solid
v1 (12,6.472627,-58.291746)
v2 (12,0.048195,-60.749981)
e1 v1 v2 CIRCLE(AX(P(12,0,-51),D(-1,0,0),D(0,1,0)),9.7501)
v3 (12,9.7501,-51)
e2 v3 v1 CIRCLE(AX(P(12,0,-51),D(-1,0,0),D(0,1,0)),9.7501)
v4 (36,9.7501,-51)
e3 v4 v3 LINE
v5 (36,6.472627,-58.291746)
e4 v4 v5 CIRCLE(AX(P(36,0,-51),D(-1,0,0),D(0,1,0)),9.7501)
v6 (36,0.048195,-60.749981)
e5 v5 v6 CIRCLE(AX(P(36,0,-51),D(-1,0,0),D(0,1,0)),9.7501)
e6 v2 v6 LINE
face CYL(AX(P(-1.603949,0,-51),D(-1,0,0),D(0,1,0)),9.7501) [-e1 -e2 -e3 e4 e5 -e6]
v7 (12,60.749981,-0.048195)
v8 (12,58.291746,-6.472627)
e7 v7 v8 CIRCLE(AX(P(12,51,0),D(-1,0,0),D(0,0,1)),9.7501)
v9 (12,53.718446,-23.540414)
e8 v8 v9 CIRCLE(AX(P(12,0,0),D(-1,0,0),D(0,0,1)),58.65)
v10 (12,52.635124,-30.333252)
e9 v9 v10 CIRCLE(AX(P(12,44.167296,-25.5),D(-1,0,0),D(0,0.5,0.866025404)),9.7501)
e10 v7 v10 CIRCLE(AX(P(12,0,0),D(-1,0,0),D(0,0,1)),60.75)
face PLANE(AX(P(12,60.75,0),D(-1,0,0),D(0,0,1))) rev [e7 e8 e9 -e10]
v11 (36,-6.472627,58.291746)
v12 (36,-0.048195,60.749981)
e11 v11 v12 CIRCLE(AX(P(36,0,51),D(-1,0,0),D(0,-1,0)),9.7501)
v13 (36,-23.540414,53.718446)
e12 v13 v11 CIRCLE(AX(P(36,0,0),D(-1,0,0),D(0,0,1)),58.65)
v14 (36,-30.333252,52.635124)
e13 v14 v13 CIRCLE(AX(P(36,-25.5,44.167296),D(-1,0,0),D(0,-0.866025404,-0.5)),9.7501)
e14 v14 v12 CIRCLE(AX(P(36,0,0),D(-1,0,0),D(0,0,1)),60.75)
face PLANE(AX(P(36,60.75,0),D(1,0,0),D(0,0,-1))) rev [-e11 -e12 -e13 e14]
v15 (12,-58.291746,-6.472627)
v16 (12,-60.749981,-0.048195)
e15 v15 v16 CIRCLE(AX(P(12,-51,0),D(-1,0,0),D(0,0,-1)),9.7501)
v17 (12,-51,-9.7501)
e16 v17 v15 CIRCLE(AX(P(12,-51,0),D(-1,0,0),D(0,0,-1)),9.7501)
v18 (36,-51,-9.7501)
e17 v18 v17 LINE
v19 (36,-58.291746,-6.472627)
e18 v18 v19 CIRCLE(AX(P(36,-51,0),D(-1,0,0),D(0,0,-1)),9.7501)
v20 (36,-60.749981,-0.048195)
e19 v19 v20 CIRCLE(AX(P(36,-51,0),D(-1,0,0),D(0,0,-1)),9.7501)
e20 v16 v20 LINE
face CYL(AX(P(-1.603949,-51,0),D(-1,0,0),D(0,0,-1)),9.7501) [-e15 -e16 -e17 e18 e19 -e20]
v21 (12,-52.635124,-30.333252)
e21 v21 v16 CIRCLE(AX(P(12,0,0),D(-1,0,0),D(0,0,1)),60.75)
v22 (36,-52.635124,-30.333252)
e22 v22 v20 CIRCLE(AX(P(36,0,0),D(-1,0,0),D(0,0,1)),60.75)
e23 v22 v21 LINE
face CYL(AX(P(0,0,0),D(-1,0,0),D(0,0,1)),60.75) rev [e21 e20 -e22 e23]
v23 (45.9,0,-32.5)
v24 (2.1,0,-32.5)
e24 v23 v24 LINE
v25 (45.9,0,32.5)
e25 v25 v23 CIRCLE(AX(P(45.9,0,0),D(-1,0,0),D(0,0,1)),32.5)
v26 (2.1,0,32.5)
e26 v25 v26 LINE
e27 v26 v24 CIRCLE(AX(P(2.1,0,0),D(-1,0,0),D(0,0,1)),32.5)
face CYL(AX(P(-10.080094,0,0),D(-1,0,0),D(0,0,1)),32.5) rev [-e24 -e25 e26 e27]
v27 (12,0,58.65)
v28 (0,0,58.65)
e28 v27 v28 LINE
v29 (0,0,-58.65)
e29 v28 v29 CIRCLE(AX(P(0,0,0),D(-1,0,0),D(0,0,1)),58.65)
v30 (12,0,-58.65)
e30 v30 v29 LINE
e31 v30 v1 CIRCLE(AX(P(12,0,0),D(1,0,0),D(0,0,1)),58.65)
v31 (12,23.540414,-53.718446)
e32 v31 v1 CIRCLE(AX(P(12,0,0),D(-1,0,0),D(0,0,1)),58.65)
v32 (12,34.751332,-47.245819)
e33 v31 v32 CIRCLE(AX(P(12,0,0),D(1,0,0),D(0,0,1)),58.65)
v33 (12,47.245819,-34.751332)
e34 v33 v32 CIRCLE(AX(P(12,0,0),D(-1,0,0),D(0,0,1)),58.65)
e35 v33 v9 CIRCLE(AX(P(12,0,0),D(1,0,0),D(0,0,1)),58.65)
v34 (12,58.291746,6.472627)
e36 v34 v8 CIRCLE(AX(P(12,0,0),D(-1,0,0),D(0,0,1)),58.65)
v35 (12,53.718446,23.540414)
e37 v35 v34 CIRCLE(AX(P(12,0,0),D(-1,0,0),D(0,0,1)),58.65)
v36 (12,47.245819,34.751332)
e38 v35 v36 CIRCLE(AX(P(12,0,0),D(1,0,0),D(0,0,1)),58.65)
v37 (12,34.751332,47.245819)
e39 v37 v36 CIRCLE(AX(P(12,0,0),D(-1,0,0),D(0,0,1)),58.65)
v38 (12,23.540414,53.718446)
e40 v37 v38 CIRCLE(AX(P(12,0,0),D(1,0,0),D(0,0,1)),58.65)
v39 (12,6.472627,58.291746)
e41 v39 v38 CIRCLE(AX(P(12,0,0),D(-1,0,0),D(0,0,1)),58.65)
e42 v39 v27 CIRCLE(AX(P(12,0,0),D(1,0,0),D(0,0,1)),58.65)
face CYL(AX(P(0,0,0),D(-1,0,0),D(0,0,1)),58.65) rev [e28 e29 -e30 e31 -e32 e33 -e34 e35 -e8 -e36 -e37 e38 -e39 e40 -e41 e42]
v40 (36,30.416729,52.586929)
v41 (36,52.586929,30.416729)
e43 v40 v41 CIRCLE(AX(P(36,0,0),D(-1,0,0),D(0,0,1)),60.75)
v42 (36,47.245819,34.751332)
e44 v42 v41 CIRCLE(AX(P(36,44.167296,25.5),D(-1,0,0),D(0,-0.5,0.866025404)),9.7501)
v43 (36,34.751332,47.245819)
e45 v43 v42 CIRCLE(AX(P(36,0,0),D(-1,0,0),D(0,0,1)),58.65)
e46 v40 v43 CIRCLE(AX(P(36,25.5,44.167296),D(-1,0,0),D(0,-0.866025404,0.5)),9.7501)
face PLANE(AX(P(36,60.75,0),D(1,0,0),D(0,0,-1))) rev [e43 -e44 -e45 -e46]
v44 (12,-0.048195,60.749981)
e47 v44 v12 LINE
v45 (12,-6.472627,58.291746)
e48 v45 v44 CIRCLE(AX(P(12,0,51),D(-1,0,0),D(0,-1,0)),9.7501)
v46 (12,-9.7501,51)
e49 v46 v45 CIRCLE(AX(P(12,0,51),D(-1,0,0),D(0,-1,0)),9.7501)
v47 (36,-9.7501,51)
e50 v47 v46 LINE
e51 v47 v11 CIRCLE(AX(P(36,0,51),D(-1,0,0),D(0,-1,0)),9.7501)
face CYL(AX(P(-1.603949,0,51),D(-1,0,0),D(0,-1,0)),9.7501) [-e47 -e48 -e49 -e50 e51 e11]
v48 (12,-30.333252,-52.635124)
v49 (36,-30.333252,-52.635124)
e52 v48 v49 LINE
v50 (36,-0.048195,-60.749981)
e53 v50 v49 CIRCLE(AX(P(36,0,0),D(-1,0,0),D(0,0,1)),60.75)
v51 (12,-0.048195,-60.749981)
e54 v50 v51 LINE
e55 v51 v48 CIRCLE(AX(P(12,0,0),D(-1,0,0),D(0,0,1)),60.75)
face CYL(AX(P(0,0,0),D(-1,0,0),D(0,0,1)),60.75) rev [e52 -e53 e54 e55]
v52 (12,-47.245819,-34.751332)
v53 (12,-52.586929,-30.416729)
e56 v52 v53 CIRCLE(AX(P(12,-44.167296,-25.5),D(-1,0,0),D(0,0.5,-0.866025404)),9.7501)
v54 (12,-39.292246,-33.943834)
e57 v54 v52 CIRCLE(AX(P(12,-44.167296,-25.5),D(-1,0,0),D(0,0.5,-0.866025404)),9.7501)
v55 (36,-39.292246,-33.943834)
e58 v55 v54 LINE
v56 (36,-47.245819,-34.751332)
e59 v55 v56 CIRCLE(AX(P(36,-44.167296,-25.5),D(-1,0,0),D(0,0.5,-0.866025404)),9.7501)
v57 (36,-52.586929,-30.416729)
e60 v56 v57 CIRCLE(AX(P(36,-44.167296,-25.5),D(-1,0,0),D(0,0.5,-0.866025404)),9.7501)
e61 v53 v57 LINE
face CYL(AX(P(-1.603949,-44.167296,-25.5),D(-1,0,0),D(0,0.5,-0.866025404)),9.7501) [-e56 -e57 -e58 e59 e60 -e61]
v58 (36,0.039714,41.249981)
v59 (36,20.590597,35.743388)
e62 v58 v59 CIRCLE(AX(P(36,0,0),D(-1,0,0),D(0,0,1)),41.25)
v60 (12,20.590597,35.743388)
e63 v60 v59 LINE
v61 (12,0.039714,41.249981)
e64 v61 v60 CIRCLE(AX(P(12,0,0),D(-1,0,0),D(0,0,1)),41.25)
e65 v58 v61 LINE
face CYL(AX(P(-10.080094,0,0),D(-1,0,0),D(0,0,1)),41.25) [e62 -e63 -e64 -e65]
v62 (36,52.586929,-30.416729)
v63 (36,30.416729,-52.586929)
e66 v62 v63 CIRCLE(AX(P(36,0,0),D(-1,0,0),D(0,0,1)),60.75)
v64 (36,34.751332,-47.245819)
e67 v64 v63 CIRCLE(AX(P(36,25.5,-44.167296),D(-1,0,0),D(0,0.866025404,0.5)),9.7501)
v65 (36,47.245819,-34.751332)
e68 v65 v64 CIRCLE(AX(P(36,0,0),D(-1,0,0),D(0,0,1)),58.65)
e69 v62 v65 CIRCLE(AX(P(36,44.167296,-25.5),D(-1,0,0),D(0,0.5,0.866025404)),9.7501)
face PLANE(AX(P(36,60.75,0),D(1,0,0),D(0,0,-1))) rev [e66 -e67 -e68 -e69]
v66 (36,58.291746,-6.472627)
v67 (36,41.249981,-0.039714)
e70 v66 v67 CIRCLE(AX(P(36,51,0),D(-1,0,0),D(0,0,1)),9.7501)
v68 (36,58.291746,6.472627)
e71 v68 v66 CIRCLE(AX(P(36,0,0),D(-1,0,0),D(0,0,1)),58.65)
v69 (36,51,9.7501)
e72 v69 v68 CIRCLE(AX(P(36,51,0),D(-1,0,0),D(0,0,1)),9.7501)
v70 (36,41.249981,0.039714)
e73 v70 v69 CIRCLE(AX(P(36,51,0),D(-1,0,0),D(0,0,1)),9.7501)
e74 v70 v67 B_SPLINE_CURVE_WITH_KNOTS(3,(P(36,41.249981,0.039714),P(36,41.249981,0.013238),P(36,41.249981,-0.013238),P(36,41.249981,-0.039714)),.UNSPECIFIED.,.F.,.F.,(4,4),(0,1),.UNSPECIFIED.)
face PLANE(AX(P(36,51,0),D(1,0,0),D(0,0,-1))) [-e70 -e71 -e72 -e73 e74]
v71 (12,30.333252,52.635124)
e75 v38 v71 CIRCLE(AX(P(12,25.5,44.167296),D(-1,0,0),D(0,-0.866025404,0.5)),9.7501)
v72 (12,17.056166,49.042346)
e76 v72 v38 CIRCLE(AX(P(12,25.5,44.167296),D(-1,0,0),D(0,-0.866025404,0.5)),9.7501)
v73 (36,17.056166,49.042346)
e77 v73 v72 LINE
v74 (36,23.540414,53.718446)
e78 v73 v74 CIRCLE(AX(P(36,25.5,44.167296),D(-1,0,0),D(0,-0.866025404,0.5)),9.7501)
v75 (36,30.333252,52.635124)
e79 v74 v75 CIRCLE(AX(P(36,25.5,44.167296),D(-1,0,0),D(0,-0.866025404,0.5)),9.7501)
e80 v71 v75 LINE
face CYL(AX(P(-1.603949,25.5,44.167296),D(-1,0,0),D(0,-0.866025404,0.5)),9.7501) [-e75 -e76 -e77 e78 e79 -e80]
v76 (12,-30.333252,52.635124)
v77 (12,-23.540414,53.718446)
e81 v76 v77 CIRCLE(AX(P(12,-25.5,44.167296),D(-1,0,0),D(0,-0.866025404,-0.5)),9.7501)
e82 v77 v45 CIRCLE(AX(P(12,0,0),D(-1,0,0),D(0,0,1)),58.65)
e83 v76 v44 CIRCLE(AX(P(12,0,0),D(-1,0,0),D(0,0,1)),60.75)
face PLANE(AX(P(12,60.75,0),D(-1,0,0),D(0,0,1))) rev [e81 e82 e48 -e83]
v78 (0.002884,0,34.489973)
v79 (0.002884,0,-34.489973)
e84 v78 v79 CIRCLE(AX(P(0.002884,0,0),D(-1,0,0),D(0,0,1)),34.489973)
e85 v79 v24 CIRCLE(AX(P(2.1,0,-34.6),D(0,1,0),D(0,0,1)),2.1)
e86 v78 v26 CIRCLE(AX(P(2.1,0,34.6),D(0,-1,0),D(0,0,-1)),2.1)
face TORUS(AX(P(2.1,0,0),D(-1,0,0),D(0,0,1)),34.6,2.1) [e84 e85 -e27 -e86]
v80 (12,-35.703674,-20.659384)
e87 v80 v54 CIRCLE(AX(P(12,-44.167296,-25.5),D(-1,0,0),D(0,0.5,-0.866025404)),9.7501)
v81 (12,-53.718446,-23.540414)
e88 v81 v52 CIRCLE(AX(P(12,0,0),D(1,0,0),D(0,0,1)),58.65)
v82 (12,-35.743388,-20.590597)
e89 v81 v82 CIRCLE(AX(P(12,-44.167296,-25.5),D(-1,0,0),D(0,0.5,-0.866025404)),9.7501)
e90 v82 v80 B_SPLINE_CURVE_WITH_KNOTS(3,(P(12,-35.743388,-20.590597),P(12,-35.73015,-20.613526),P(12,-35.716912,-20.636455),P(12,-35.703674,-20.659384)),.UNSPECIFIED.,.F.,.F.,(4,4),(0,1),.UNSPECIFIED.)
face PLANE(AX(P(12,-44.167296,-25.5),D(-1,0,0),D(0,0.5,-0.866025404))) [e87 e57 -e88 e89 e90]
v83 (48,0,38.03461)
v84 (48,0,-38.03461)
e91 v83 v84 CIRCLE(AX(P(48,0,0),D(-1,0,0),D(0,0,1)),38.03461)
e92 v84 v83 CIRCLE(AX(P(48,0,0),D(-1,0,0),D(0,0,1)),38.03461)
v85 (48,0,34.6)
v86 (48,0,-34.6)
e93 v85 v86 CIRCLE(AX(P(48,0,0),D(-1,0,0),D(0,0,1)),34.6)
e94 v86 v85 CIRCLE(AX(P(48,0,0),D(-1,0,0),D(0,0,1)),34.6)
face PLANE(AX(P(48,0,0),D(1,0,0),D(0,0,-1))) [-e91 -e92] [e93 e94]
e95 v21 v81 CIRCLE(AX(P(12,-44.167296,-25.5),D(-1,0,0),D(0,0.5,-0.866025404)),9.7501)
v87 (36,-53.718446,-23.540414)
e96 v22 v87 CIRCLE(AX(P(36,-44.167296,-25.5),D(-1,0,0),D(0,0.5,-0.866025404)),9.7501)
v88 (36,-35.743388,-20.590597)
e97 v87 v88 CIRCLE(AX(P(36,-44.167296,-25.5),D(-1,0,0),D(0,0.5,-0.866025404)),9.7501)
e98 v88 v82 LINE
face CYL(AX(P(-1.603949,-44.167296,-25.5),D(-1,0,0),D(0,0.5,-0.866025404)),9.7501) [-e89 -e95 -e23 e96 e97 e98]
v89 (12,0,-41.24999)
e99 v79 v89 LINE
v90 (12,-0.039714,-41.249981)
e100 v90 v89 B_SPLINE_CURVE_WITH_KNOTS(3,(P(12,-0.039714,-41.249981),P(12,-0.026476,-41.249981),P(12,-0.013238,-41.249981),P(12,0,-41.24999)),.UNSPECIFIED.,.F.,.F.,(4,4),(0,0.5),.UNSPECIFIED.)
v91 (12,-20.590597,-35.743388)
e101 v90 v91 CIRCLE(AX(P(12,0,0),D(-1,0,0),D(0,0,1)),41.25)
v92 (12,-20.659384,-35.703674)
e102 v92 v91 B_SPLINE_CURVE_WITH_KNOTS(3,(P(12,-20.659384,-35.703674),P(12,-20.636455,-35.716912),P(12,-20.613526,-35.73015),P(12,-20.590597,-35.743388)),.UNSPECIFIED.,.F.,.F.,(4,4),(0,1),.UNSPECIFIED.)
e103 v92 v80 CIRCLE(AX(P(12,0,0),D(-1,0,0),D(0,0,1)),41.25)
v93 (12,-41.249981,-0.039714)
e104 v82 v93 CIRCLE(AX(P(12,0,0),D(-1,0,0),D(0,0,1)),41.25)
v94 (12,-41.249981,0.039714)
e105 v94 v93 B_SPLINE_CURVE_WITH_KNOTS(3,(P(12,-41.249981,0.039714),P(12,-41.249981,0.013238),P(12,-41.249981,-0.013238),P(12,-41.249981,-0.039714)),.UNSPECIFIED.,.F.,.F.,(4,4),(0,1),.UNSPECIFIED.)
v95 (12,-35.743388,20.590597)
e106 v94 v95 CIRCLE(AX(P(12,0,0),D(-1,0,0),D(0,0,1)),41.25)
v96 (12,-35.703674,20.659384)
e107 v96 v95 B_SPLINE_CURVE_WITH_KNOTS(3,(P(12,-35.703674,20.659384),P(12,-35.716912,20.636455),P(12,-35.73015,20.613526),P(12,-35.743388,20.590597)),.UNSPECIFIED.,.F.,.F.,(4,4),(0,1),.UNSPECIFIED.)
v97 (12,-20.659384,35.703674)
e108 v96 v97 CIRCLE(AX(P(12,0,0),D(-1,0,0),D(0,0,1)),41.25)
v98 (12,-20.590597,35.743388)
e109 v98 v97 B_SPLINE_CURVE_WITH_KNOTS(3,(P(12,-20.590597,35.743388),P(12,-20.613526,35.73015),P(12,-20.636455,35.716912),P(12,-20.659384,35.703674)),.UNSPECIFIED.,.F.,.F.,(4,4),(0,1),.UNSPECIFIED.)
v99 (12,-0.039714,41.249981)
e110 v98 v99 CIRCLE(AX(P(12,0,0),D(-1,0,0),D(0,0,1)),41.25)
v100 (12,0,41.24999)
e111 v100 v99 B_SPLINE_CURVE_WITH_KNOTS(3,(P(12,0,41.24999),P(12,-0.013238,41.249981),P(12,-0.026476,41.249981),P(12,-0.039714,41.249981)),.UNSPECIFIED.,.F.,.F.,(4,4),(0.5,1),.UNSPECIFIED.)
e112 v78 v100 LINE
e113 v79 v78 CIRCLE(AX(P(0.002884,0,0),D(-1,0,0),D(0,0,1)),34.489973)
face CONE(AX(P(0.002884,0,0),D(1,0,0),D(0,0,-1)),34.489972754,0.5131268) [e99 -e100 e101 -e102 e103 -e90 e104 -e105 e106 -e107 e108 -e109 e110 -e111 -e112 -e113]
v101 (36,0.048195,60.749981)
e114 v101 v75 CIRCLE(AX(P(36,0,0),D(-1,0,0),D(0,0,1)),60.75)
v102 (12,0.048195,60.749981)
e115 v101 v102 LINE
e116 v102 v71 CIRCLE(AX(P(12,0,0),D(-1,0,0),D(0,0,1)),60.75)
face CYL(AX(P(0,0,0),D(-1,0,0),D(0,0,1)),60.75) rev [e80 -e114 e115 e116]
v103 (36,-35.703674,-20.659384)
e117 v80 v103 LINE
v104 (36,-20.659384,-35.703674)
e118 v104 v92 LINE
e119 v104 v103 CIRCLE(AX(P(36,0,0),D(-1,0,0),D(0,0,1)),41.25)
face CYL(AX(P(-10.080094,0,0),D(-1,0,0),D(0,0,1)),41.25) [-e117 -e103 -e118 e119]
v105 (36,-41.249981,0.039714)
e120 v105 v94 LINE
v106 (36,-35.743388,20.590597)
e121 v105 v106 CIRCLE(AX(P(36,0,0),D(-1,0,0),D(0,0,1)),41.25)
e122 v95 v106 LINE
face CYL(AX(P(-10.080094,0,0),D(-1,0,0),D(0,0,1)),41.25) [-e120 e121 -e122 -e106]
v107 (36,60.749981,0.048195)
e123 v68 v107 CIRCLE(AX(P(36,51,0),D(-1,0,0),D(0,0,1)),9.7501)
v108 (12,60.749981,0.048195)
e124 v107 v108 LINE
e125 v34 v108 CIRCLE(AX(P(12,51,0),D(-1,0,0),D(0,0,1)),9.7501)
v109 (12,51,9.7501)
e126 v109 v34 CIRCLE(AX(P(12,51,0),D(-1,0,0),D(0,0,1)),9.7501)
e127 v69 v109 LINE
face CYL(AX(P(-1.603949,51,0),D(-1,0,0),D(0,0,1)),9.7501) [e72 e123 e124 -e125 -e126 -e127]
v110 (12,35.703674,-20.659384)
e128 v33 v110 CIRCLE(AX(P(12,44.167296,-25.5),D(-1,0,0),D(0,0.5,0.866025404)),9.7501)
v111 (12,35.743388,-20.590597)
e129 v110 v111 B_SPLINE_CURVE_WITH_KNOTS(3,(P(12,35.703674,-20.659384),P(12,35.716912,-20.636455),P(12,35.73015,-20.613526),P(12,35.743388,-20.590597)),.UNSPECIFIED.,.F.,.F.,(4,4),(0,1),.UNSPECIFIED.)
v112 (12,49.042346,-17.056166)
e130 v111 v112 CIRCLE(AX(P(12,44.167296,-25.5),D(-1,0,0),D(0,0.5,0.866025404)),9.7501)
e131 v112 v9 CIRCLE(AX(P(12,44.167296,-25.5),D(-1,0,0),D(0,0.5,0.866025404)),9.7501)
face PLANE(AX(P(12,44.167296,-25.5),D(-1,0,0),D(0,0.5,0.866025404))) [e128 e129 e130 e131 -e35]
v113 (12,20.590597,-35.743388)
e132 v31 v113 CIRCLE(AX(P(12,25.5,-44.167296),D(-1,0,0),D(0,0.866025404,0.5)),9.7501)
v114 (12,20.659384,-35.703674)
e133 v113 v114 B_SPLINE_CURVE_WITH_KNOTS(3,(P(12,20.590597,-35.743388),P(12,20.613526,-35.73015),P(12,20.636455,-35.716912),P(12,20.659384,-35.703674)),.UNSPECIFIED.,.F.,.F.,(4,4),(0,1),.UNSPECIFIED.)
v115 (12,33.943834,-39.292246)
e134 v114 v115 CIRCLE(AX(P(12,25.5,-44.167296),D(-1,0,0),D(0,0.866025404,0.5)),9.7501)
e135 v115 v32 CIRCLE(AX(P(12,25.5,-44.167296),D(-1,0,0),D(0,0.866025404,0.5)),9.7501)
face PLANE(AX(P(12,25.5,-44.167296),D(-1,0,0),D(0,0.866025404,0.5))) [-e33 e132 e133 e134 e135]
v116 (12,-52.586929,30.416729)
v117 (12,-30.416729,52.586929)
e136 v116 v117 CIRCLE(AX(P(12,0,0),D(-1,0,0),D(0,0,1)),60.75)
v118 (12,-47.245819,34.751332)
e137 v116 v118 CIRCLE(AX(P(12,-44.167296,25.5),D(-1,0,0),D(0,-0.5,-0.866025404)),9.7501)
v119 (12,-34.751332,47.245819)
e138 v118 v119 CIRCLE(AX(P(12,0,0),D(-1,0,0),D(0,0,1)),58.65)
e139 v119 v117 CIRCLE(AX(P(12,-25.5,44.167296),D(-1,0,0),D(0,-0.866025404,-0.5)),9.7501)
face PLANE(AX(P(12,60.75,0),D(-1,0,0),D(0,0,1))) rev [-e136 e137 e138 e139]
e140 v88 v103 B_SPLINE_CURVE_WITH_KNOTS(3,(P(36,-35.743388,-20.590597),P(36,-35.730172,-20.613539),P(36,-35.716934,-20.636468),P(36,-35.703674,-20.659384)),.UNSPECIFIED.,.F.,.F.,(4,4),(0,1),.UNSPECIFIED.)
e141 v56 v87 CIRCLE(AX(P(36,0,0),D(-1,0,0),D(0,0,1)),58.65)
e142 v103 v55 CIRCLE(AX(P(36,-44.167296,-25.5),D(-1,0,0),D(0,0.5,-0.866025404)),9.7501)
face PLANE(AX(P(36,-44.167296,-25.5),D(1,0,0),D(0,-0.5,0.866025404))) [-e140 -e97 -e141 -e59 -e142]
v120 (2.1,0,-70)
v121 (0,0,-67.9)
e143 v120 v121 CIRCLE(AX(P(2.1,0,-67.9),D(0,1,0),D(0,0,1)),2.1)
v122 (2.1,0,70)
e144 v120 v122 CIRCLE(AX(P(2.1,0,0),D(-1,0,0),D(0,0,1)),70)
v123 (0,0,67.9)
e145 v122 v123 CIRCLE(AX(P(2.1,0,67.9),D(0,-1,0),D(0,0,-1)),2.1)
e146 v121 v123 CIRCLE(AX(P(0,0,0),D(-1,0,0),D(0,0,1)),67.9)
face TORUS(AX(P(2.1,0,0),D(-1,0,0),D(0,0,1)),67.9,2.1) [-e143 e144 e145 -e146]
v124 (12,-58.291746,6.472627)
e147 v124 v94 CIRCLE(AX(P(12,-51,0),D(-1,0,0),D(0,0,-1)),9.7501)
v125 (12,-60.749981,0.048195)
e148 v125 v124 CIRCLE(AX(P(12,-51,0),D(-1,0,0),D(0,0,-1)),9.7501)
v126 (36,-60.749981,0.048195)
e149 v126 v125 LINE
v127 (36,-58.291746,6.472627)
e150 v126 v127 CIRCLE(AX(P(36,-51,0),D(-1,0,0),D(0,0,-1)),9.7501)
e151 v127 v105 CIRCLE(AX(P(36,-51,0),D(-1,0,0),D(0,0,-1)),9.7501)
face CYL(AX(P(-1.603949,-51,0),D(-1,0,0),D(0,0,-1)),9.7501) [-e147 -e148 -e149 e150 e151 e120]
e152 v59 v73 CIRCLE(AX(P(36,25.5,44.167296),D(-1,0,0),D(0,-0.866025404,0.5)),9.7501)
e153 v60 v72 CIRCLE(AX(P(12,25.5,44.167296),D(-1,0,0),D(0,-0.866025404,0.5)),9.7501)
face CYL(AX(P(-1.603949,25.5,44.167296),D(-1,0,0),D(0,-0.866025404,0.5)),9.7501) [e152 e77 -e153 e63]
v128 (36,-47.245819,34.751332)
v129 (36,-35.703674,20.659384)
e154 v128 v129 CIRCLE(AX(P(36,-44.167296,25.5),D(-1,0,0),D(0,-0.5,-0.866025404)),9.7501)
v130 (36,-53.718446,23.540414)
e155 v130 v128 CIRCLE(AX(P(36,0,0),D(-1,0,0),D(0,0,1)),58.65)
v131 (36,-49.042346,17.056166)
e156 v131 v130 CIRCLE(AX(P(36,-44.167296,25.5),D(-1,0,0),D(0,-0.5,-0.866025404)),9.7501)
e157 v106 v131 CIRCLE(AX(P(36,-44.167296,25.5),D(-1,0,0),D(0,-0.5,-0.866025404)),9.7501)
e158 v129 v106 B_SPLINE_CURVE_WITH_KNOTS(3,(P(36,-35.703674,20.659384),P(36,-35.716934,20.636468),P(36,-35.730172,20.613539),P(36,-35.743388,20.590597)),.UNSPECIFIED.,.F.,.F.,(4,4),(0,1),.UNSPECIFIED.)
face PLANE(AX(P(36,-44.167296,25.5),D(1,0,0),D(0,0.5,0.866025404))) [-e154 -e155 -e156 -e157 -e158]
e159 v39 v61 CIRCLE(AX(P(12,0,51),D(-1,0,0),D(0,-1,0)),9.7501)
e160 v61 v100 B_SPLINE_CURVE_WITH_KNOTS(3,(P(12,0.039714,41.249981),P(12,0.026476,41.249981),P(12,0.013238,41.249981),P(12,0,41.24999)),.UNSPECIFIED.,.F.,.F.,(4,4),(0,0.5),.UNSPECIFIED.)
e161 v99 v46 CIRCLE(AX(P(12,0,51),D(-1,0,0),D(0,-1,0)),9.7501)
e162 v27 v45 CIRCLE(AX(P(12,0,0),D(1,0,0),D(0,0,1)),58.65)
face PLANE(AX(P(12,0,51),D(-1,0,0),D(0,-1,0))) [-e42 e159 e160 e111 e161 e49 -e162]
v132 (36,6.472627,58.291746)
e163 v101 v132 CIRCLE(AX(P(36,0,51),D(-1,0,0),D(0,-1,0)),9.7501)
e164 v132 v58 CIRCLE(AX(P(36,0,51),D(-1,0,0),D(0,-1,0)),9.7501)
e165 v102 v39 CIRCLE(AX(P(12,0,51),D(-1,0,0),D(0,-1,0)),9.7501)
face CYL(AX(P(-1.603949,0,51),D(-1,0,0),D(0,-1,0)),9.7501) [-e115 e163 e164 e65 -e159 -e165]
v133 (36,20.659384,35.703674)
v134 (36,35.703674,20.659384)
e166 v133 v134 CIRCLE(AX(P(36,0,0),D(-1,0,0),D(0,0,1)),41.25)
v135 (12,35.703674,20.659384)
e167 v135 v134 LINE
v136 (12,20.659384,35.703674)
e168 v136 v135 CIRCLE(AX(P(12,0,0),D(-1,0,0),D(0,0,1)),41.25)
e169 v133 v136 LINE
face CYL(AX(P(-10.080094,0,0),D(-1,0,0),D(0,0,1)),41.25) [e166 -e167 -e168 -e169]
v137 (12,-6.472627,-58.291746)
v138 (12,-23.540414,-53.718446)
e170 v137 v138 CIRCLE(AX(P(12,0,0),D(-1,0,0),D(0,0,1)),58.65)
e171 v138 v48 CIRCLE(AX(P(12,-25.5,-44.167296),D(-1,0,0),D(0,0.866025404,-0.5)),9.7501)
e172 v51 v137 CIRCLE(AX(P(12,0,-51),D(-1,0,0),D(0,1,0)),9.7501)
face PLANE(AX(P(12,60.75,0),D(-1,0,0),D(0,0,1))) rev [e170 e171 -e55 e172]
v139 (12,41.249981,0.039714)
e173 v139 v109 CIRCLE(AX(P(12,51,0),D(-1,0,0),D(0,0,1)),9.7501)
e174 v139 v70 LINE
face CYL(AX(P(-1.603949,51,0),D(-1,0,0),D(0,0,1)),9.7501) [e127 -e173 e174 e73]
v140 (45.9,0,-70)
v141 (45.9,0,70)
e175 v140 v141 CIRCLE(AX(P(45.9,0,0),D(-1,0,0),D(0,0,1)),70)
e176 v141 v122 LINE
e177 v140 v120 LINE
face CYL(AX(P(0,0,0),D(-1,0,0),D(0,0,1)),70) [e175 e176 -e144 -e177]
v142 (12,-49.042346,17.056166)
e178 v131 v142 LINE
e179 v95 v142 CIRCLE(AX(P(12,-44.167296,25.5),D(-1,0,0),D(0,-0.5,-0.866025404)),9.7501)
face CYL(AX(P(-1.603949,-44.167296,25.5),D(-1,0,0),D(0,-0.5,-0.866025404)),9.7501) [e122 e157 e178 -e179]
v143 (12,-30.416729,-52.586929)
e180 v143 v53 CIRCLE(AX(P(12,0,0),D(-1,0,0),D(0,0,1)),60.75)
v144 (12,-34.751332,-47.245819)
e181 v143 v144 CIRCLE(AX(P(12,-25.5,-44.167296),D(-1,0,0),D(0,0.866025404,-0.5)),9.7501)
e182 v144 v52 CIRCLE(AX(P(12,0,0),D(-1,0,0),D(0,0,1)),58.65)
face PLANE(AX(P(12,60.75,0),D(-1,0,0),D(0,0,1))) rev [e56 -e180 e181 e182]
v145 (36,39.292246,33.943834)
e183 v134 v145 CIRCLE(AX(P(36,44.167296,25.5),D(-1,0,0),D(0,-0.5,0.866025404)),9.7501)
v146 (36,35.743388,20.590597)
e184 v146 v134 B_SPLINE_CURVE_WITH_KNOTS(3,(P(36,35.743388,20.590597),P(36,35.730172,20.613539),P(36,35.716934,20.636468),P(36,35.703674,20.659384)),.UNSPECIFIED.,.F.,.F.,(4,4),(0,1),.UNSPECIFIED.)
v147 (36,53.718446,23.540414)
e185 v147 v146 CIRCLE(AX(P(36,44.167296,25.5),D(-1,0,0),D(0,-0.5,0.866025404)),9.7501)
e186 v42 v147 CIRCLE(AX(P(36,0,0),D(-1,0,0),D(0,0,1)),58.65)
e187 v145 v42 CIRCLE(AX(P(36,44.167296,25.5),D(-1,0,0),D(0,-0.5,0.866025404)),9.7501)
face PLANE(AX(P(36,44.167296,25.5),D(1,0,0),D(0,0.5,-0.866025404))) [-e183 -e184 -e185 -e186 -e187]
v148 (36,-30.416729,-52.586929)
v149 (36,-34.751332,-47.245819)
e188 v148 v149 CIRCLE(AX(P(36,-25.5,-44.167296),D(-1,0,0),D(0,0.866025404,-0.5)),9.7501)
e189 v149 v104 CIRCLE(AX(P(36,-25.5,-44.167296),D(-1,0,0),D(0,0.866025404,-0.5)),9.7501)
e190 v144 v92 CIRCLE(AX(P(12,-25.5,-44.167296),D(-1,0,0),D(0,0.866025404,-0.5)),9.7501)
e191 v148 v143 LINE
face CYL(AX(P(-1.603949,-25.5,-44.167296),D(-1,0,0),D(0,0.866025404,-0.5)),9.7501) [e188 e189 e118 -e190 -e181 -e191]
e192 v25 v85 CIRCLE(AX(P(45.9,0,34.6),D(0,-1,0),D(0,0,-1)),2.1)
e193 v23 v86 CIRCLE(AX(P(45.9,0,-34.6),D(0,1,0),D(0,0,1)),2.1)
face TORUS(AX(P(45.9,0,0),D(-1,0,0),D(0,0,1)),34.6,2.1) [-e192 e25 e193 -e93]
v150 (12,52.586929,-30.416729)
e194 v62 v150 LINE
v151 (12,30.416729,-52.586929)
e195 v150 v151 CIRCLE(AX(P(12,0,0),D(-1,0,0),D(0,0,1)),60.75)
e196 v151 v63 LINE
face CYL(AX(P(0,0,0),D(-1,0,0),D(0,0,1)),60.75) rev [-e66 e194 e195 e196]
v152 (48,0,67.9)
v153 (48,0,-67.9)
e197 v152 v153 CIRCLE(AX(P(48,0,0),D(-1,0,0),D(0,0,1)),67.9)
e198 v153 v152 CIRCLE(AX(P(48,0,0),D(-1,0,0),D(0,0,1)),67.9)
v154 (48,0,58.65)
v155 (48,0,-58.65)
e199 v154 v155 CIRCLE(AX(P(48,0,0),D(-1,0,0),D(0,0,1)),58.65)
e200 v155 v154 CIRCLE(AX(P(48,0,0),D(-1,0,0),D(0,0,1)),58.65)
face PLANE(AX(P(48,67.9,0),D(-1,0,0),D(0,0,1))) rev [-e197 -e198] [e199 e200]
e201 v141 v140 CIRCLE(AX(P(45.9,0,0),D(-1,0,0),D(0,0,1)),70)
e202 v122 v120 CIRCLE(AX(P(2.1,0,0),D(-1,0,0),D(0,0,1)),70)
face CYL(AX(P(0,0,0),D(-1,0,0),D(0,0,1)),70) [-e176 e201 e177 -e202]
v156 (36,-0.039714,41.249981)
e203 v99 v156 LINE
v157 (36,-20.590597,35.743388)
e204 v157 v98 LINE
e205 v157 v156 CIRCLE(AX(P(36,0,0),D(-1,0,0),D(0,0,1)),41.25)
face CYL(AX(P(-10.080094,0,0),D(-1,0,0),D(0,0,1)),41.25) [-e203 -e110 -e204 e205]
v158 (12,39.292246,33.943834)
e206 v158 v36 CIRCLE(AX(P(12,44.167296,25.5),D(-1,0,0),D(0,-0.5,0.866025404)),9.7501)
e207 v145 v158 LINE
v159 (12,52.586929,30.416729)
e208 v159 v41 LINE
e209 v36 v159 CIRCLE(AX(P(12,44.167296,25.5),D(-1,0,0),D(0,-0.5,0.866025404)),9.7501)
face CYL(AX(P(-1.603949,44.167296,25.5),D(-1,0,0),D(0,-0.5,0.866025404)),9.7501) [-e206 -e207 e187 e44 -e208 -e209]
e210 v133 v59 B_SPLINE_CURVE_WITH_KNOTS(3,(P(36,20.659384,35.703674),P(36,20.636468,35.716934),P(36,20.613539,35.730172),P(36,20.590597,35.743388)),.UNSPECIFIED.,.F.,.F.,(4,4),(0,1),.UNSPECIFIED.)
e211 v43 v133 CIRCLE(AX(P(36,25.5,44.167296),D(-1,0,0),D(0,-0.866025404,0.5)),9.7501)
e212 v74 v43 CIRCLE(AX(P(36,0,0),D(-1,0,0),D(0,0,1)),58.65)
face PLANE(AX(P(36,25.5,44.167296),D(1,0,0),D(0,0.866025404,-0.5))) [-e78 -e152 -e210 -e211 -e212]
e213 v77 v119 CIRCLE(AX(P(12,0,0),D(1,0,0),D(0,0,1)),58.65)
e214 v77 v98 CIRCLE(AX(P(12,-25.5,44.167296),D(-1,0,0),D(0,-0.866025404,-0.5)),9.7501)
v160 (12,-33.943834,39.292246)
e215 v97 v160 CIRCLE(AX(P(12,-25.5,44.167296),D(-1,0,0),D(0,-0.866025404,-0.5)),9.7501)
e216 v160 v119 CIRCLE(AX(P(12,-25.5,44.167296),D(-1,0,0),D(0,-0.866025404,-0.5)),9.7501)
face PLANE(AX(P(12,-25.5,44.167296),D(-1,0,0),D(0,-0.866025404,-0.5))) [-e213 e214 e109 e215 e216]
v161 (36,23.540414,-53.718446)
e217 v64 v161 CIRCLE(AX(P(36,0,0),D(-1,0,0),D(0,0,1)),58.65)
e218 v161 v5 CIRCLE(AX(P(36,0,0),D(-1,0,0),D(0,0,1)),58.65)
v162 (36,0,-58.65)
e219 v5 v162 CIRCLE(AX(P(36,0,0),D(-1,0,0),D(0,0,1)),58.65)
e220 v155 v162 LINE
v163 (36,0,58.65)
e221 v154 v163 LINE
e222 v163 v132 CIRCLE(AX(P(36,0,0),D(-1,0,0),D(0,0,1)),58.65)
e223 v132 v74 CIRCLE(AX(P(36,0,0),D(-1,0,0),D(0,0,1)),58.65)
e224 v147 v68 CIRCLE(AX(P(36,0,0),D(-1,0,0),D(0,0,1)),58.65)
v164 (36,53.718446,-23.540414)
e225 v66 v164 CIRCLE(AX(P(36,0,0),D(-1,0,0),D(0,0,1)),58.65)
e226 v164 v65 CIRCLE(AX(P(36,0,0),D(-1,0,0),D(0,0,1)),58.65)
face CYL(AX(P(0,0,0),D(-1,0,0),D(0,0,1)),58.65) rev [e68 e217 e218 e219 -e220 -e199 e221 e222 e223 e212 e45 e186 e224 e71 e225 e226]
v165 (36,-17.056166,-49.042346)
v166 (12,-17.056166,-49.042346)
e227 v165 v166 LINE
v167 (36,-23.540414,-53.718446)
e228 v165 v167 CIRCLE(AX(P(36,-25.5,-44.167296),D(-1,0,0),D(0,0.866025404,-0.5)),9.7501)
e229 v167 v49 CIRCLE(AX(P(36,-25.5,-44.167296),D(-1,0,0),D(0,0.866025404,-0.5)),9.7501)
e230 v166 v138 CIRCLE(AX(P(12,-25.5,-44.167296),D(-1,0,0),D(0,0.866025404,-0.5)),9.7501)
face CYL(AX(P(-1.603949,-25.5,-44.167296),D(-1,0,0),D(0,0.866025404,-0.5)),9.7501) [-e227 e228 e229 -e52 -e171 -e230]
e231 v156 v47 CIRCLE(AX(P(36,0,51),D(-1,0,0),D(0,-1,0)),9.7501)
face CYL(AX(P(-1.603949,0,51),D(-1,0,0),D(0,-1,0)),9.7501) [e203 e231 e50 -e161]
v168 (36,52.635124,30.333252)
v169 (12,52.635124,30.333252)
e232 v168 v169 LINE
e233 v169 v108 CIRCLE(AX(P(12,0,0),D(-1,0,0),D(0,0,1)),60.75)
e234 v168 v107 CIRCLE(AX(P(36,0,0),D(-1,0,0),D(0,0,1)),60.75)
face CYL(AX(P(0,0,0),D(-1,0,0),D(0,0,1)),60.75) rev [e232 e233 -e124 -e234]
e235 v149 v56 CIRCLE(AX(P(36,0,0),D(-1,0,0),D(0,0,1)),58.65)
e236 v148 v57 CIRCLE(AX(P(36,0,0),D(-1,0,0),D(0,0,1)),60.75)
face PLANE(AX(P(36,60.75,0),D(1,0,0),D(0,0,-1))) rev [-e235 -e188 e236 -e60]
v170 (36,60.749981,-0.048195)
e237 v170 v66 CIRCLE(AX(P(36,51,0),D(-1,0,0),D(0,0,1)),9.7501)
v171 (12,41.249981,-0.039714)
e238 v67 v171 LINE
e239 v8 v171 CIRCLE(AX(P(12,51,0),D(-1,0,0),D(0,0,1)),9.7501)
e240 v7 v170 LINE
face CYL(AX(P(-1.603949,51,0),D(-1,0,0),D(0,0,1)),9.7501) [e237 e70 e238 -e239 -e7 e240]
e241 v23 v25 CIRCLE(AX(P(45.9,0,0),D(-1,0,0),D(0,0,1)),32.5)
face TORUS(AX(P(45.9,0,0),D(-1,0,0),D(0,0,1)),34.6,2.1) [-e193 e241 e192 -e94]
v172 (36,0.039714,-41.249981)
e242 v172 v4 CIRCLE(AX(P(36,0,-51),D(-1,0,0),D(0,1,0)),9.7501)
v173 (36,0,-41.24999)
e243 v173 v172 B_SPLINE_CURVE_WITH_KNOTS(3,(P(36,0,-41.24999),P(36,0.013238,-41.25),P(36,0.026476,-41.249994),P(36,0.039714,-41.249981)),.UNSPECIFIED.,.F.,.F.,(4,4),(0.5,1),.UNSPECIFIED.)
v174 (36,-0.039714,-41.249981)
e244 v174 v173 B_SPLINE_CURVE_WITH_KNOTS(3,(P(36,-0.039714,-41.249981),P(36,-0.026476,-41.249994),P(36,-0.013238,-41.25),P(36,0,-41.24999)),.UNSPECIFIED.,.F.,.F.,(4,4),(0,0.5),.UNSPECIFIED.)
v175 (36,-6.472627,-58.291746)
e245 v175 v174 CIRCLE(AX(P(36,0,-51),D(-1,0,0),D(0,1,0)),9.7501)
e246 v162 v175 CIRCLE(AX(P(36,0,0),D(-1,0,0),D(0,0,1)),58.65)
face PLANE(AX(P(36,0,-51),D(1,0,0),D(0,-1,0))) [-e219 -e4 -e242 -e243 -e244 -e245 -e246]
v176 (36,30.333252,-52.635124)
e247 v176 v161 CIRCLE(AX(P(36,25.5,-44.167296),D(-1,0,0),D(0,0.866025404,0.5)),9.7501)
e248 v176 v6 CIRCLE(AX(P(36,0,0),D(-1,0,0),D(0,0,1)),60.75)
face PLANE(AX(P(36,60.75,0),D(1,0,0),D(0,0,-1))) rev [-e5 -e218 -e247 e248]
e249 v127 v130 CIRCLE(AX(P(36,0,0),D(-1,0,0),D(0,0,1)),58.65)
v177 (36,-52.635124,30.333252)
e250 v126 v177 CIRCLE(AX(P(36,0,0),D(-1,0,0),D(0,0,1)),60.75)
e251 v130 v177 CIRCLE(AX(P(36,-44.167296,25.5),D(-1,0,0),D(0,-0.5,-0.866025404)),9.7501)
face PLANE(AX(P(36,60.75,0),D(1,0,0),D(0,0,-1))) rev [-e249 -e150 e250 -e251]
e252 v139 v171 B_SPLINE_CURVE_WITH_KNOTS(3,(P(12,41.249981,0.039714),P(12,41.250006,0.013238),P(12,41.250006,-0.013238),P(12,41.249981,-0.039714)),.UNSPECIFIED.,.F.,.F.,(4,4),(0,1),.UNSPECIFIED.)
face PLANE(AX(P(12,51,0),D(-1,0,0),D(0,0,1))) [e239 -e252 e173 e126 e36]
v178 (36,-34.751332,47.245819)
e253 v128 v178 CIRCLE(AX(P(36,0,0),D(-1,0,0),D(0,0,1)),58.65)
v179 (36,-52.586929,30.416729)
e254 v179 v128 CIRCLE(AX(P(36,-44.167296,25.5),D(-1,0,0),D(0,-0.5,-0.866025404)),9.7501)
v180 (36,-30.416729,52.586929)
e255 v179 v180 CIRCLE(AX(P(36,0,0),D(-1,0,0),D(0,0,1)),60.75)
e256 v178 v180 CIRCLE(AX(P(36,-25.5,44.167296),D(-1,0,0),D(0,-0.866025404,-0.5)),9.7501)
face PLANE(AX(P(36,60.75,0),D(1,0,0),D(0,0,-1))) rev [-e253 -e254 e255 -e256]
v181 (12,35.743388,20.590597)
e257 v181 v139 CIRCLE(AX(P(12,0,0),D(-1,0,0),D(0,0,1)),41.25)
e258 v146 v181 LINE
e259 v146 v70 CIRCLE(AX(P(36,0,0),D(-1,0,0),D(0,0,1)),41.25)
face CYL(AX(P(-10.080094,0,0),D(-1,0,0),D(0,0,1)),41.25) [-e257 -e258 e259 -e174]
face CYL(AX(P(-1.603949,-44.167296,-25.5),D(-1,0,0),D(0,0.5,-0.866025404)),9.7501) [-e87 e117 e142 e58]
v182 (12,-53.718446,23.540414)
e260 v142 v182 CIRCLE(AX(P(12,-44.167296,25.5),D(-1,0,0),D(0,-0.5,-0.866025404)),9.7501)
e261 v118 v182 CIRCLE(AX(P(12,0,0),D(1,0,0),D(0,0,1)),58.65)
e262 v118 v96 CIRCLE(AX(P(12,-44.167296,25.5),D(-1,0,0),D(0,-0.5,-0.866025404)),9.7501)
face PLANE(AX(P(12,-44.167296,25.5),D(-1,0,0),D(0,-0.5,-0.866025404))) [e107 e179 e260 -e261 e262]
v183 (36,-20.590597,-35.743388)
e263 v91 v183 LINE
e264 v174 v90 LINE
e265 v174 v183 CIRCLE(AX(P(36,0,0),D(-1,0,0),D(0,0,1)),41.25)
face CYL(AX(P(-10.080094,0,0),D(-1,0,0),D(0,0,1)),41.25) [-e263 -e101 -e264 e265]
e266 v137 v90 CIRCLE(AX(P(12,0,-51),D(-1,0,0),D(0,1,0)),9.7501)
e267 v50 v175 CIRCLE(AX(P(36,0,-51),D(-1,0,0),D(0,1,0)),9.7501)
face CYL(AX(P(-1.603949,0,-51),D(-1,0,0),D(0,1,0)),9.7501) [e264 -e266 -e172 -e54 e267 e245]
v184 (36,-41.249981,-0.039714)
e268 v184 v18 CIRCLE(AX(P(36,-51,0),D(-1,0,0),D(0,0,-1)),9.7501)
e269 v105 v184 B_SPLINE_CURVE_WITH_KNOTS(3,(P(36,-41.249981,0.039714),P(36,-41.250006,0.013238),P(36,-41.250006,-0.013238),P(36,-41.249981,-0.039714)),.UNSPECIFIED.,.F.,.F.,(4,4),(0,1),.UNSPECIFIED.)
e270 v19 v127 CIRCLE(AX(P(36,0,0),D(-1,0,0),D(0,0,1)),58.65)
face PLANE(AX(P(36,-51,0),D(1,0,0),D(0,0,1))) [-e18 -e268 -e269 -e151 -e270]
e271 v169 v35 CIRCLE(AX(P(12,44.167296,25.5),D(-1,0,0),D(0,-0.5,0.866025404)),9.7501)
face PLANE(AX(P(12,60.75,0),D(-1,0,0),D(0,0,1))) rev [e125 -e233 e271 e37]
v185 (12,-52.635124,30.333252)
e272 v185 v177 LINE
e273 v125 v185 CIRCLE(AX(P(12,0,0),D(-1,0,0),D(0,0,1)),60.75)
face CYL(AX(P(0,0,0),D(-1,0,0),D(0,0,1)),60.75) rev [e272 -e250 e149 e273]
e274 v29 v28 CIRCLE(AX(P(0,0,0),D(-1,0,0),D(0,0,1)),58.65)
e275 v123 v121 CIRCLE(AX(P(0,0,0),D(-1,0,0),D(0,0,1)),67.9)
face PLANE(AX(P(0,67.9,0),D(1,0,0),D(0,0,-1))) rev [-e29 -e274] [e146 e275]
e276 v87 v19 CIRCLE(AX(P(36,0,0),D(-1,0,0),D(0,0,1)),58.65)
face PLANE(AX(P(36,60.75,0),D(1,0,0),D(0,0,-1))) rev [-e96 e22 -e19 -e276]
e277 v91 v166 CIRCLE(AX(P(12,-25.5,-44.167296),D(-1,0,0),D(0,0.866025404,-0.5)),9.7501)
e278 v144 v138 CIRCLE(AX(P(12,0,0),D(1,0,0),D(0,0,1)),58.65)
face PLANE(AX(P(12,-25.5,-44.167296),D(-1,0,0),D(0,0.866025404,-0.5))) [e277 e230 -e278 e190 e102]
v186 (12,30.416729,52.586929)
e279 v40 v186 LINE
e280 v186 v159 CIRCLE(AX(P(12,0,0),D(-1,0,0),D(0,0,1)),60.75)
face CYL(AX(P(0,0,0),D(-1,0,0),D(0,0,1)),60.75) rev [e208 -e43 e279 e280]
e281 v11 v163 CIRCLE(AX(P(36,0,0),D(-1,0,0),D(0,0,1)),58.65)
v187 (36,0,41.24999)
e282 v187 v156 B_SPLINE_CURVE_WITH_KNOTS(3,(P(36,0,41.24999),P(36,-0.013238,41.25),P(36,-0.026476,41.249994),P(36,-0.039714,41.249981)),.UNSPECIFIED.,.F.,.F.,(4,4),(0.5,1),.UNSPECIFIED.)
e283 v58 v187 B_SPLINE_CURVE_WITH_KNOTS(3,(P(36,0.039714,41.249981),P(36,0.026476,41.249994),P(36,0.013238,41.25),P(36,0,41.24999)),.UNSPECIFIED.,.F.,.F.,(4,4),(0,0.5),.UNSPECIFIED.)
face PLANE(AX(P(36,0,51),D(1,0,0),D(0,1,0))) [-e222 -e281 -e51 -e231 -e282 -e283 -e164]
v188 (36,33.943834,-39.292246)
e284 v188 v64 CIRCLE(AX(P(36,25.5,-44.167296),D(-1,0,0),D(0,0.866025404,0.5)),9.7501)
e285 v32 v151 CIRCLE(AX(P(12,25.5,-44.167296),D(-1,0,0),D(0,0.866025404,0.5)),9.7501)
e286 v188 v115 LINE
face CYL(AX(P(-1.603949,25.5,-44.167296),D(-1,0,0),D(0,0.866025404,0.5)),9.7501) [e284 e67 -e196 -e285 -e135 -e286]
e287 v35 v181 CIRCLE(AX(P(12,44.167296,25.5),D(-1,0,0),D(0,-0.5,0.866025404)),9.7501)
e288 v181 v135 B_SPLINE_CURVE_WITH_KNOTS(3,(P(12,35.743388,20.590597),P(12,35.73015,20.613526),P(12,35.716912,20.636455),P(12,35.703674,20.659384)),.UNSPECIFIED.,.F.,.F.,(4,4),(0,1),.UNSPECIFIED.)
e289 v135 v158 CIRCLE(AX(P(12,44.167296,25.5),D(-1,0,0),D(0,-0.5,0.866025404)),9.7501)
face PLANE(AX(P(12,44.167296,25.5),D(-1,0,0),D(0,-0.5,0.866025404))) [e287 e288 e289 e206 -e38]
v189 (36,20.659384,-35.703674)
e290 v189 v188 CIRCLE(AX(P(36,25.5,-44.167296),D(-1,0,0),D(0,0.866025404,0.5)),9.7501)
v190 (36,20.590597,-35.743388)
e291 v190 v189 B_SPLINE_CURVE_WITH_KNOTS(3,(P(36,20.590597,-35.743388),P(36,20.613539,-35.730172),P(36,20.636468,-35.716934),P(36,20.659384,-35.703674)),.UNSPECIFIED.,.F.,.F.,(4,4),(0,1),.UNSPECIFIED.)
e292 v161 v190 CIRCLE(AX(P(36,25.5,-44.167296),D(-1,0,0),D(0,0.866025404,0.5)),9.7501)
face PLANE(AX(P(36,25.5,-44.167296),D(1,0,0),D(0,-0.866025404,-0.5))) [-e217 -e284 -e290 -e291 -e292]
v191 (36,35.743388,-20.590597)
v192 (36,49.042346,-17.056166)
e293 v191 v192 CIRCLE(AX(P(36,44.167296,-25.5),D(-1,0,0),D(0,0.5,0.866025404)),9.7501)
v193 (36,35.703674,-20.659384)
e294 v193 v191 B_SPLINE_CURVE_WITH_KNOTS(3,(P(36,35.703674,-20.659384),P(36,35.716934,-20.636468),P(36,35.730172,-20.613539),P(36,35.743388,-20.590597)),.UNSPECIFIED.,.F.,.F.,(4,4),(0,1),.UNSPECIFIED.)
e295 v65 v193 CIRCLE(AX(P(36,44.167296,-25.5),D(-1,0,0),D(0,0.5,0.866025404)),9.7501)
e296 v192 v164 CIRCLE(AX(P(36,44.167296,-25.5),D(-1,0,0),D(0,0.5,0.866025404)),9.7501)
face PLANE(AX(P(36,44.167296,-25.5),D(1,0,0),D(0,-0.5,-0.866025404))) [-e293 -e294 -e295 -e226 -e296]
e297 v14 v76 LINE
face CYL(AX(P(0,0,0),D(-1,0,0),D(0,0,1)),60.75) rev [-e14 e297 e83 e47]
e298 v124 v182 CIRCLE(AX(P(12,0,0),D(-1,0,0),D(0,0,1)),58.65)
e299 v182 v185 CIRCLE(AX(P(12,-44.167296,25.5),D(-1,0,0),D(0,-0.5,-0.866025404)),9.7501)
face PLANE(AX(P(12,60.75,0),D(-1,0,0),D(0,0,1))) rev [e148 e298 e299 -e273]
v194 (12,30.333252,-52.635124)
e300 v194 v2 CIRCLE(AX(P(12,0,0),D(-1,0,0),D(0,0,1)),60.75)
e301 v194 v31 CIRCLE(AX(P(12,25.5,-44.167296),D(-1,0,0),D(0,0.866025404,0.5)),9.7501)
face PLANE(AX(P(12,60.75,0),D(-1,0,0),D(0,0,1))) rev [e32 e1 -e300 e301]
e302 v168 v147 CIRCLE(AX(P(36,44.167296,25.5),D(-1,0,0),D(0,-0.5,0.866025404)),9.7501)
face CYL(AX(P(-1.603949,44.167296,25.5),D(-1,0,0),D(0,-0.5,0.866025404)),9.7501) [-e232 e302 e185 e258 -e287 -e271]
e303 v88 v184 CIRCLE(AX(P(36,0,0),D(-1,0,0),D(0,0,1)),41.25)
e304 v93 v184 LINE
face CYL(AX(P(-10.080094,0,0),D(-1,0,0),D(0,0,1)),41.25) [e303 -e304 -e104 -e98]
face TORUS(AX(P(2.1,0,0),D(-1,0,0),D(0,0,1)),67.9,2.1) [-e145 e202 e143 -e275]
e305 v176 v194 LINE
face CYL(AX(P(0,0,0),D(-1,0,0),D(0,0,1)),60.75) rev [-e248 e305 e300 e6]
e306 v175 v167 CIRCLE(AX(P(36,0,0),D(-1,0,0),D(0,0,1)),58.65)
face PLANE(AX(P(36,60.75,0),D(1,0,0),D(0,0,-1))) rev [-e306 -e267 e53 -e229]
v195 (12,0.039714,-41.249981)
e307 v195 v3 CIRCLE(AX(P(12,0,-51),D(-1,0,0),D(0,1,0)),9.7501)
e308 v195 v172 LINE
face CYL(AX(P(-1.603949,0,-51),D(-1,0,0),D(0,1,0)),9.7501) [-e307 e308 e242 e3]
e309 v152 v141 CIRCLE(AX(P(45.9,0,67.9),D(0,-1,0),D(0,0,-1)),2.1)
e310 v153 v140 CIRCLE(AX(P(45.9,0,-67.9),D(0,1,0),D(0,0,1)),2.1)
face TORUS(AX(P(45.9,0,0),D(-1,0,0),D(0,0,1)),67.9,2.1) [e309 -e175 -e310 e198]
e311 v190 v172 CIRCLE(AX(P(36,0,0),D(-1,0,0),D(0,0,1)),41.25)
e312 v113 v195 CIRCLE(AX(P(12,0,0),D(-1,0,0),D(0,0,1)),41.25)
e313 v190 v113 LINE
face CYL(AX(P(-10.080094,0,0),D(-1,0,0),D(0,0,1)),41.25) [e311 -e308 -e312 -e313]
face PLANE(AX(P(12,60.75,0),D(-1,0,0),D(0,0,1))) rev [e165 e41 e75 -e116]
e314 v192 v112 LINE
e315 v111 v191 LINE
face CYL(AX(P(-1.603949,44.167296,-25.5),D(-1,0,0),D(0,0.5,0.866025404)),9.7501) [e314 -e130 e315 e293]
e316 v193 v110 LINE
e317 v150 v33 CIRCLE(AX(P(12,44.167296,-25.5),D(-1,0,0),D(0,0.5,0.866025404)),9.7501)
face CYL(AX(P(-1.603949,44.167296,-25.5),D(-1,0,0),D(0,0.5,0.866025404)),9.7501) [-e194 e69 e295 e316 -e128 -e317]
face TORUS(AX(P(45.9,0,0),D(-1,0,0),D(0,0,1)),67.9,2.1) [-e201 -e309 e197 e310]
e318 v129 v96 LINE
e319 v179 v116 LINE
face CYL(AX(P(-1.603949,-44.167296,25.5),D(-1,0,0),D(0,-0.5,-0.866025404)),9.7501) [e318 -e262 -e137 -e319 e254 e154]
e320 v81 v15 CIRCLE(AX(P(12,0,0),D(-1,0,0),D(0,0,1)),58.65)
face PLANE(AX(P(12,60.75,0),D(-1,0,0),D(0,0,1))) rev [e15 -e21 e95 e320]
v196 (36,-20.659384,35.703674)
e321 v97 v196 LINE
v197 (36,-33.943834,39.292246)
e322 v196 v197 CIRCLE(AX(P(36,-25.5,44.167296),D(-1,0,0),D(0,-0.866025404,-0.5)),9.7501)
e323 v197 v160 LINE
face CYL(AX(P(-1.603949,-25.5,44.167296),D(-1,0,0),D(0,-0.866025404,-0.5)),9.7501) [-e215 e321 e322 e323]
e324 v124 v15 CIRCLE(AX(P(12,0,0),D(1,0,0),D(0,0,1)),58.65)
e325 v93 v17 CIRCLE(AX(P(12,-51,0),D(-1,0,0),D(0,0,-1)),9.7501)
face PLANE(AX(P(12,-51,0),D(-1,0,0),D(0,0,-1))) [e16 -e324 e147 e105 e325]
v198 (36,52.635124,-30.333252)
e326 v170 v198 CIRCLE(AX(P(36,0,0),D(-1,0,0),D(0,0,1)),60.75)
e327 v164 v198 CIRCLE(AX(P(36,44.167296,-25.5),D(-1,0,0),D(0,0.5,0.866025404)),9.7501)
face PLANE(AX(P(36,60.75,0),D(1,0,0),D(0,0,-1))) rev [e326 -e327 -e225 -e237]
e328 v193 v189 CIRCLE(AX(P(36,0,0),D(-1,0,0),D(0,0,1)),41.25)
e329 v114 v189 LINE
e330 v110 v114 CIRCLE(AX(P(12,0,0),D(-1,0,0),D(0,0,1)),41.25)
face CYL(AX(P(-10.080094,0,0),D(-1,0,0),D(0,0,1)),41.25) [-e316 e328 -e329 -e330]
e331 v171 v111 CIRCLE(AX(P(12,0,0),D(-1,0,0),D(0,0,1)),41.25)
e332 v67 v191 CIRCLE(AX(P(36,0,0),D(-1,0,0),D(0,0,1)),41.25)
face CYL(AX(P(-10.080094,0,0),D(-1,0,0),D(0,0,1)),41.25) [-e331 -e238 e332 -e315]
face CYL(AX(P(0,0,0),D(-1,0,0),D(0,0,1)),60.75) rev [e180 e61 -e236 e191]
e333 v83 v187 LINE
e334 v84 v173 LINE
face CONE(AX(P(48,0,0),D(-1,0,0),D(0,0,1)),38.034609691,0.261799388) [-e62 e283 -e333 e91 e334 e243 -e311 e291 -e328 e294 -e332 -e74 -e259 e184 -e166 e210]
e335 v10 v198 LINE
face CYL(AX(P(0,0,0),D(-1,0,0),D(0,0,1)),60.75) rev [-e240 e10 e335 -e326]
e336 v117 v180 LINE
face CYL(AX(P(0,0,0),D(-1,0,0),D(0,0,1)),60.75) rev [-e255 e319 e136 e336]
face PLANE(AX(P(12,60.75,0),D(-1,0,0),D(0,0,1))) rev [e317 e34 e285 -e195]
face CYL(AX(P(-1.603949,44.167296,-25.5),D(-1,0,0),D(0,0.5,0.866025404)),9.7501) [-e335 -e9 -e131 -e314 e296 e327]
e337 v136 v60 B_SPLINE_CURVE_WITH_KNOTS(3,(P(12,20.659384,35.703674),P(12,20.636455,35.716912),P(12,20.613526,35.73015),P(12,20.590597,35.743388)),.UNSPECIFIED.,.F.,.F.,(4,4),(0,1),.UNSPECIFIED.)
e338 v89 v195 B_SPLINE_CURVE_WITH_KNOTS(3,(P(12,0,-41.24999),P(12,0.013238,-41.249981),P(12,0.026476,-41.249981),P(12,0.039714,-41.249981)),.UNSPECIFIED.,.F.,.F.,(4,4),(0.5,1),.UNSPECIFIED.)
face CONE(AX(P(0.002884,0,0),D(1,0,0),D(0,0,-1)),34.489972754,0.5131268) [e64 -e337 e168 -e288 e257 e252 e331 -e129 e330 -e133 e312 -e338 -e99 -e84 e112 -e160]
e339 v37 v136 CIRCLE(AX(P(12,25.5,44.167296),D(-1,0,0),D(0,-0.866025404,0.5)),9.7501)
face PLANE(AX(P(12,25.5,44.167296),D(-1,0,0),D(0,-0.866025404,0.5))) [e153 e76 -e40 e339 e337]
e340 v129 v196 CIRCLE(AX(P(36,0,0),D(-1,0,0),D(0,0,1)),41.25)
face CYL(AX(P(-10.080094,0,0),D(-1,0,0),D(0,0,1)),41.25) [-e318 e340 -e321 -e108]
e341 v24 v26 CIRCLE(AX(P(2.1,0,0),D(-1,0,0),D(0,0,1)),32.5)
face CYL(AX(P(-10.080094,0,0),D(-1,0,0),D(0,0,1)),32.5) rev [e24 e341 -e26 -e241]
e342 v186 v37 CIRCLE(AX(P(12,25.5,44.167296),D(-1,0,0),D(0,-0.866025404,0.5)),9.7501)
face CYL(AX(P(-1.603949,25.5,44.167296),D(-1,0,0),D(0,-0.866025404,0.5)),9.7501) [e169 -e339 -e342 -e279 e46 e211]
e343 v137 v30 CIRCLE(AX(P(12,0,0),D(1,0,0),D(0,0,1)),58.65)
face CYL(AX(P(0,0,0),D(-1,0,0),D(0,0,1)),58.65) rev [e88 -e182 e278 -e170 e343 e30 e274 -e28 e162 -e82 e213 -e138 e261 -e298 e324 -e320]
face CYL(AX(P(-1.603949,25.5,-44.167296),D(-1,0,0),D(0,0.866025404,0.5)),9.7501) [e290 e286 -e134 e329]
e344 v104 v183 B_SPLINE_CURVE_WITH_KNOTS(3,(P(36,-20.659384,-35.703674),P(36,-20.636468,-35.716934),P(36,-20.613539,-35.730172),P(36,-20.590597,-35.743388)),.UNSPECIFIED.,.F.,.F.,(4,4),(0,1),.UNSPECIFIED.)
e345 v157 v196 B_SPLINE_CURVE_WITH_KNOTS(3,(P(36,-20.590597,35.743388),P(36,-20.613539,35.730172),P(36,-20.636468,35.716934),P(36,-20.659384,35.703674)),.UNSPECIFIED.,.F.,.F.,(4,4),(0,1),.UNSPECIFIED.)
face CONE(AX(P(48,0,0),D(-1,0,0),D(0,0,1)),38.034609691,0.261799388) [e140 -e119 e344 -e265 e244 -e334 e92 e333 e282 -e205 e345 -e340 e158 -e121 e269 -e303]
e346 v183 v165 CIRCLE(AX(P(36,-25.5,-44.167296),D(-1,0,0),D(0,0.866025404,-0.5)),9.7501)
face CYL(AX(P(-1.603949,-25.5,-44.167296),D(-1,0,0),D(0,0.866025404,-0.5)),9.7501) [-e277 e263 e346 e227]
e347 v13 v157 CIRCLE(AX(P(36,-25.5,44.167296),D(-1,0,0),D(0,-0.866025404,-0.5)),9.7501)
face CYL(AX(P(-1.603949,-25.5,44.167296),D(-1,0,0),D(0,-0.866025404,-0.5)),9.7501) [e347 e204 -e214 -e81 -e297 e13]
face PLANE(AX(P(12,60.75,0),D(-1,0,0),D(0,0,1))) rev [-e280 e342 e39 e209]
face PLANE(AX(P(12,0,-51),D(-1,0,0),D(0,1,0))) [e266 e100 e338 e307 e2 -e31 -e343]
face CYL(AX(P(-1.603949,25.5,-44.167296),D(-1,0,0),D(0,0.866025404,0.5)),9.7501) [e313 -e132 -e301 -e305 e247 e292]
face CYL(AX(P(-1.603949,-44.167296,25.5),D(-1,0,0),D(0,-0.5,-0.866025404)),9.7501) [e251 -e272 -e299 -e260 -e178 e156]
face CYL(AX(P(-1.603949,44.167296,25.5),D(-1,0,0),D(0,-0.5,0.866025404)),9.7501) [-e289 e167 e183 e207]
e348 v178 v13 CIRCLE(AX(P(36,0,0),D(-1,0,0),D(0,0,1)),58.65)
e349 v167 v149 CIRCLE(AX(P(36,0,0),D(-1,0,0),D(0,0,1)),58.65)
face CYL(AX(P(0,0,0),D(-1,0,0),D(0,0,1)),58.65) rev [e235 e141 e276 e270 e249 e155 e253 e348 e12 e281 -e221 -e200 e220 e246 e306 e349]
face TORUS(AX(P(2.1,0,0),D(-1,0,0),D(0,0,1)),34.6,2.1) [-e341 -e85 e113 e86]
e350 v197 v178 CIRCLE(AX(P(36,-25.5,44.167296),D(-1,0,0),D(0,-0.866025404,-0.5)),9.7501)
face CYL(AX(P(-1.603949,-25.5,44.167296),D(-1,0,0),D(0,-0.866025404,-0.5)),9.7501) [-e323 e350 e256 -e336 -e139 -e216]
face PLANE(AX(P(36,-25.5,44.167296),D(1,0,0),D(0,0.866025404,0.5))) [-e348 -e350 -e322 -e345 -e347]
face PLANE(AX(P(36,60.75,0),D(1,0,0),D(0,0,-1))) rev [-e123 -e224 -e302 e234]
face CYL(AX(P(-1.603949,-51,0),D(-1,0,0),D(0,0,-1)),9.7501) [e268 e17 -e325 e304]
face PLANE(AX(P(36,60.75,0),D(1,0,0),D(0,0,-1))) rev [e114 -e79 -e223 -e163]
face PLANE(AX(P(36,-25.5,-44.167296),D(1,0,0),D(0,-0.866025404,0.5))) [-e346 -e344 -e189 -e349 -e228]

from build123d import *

# Parameters (mm, degrees)
SKETCH3_W         = 24
SKETCH3_H         = 9.7501
CIRPATTERN1_COUNT = 12


with BuildPart() as part:
    # Sketch2 → Base-Revolve (revolve)
    with BuildSketch(Plane.XY, mode=Mode.PRIVATE) as base_revolve_sk:
        with BuildLine():
            Line((36, 41.25), (12, 41.25))
            Line((12, 41.25), (0.002884361, 34.489972754))
            ThreePointArc((0.002884361, 34.489972754), (0.654499605, 33.076671865), (2.1, 32.5))
            Line((2.1, 32.5), (45.9, 32.5))
            ThreePointArc((45.9, 32.5), (47.38492424, 33.11507576), (48, 34.6))
            Line((48, 34.6), (48, 38.034609691))
            Line((48, 38.034609691), (36, 41.25))
        make_face()
    revolve(base_revolve_sk.sketch.rotate(Axis((-10.080094127, 0, 0), (1, 0, 0)), 90), axis=Axis((-10.080094127, 0, 0), (1, 0, 0)))

    # Sketch3 → Boss-Revolve1 (revolve)
    with BuildSketch(Plane.XY):
        with Locations((24, 46.12495)):
            Rectangle(SKETCH3_W, SKETCH3_H)
    boss_revolve1 = revolve(axis=Axis((-1.603948851, 51, 0), (1, 0, 0)))

    # Sketch4 → Boss-Revolve2 (revolve)
    with BuildSketch(Plane.XY, mode=Mode.PRIVATE) as boss_revolve2_sk:
        with BuildLine():
            Line((36, 58.65), (48, 58.65))
            Line((48, 58.65), (48, 67.9))
            ThreePointArc((48, 67.9), (47.38492424, 69.38492424), (45.9, 70))
            Line((45.9, 70), (2.1, 70))
            ThreePointArc((2.1, 70), (0.61507576, 69.38492424), (0, 67.9))
            Line((0, 67.9), (0, 58.65))
            Line((0, 58.65), (12, 58.65))
            Line((12, 58.65), (12, 60.75))
            Line((12, 60.75), (36, 60.75))
            Line((36, 60.75), (36, 58.65))
        make_face()
    revolve(boss_revolve2_sk.sketch.rotate(Axis((0, 0, 0), (1, 0, 0)), 90), axis=Axis((0, 0, 0), (1, 0, 0)))

    # CirPattern1: Boss-Revolve1 ×12 about axis
    cirpattern1_axis = Axis((0, 0, 0), (1, 0, 0))
    for i in range(1, CIRPATTERN1_COUNT):
        add(boss_revolve1.rotate(cirpattern1_axis, i * 360 / CIRPATTERN1_COUNT))


solid = part.part
